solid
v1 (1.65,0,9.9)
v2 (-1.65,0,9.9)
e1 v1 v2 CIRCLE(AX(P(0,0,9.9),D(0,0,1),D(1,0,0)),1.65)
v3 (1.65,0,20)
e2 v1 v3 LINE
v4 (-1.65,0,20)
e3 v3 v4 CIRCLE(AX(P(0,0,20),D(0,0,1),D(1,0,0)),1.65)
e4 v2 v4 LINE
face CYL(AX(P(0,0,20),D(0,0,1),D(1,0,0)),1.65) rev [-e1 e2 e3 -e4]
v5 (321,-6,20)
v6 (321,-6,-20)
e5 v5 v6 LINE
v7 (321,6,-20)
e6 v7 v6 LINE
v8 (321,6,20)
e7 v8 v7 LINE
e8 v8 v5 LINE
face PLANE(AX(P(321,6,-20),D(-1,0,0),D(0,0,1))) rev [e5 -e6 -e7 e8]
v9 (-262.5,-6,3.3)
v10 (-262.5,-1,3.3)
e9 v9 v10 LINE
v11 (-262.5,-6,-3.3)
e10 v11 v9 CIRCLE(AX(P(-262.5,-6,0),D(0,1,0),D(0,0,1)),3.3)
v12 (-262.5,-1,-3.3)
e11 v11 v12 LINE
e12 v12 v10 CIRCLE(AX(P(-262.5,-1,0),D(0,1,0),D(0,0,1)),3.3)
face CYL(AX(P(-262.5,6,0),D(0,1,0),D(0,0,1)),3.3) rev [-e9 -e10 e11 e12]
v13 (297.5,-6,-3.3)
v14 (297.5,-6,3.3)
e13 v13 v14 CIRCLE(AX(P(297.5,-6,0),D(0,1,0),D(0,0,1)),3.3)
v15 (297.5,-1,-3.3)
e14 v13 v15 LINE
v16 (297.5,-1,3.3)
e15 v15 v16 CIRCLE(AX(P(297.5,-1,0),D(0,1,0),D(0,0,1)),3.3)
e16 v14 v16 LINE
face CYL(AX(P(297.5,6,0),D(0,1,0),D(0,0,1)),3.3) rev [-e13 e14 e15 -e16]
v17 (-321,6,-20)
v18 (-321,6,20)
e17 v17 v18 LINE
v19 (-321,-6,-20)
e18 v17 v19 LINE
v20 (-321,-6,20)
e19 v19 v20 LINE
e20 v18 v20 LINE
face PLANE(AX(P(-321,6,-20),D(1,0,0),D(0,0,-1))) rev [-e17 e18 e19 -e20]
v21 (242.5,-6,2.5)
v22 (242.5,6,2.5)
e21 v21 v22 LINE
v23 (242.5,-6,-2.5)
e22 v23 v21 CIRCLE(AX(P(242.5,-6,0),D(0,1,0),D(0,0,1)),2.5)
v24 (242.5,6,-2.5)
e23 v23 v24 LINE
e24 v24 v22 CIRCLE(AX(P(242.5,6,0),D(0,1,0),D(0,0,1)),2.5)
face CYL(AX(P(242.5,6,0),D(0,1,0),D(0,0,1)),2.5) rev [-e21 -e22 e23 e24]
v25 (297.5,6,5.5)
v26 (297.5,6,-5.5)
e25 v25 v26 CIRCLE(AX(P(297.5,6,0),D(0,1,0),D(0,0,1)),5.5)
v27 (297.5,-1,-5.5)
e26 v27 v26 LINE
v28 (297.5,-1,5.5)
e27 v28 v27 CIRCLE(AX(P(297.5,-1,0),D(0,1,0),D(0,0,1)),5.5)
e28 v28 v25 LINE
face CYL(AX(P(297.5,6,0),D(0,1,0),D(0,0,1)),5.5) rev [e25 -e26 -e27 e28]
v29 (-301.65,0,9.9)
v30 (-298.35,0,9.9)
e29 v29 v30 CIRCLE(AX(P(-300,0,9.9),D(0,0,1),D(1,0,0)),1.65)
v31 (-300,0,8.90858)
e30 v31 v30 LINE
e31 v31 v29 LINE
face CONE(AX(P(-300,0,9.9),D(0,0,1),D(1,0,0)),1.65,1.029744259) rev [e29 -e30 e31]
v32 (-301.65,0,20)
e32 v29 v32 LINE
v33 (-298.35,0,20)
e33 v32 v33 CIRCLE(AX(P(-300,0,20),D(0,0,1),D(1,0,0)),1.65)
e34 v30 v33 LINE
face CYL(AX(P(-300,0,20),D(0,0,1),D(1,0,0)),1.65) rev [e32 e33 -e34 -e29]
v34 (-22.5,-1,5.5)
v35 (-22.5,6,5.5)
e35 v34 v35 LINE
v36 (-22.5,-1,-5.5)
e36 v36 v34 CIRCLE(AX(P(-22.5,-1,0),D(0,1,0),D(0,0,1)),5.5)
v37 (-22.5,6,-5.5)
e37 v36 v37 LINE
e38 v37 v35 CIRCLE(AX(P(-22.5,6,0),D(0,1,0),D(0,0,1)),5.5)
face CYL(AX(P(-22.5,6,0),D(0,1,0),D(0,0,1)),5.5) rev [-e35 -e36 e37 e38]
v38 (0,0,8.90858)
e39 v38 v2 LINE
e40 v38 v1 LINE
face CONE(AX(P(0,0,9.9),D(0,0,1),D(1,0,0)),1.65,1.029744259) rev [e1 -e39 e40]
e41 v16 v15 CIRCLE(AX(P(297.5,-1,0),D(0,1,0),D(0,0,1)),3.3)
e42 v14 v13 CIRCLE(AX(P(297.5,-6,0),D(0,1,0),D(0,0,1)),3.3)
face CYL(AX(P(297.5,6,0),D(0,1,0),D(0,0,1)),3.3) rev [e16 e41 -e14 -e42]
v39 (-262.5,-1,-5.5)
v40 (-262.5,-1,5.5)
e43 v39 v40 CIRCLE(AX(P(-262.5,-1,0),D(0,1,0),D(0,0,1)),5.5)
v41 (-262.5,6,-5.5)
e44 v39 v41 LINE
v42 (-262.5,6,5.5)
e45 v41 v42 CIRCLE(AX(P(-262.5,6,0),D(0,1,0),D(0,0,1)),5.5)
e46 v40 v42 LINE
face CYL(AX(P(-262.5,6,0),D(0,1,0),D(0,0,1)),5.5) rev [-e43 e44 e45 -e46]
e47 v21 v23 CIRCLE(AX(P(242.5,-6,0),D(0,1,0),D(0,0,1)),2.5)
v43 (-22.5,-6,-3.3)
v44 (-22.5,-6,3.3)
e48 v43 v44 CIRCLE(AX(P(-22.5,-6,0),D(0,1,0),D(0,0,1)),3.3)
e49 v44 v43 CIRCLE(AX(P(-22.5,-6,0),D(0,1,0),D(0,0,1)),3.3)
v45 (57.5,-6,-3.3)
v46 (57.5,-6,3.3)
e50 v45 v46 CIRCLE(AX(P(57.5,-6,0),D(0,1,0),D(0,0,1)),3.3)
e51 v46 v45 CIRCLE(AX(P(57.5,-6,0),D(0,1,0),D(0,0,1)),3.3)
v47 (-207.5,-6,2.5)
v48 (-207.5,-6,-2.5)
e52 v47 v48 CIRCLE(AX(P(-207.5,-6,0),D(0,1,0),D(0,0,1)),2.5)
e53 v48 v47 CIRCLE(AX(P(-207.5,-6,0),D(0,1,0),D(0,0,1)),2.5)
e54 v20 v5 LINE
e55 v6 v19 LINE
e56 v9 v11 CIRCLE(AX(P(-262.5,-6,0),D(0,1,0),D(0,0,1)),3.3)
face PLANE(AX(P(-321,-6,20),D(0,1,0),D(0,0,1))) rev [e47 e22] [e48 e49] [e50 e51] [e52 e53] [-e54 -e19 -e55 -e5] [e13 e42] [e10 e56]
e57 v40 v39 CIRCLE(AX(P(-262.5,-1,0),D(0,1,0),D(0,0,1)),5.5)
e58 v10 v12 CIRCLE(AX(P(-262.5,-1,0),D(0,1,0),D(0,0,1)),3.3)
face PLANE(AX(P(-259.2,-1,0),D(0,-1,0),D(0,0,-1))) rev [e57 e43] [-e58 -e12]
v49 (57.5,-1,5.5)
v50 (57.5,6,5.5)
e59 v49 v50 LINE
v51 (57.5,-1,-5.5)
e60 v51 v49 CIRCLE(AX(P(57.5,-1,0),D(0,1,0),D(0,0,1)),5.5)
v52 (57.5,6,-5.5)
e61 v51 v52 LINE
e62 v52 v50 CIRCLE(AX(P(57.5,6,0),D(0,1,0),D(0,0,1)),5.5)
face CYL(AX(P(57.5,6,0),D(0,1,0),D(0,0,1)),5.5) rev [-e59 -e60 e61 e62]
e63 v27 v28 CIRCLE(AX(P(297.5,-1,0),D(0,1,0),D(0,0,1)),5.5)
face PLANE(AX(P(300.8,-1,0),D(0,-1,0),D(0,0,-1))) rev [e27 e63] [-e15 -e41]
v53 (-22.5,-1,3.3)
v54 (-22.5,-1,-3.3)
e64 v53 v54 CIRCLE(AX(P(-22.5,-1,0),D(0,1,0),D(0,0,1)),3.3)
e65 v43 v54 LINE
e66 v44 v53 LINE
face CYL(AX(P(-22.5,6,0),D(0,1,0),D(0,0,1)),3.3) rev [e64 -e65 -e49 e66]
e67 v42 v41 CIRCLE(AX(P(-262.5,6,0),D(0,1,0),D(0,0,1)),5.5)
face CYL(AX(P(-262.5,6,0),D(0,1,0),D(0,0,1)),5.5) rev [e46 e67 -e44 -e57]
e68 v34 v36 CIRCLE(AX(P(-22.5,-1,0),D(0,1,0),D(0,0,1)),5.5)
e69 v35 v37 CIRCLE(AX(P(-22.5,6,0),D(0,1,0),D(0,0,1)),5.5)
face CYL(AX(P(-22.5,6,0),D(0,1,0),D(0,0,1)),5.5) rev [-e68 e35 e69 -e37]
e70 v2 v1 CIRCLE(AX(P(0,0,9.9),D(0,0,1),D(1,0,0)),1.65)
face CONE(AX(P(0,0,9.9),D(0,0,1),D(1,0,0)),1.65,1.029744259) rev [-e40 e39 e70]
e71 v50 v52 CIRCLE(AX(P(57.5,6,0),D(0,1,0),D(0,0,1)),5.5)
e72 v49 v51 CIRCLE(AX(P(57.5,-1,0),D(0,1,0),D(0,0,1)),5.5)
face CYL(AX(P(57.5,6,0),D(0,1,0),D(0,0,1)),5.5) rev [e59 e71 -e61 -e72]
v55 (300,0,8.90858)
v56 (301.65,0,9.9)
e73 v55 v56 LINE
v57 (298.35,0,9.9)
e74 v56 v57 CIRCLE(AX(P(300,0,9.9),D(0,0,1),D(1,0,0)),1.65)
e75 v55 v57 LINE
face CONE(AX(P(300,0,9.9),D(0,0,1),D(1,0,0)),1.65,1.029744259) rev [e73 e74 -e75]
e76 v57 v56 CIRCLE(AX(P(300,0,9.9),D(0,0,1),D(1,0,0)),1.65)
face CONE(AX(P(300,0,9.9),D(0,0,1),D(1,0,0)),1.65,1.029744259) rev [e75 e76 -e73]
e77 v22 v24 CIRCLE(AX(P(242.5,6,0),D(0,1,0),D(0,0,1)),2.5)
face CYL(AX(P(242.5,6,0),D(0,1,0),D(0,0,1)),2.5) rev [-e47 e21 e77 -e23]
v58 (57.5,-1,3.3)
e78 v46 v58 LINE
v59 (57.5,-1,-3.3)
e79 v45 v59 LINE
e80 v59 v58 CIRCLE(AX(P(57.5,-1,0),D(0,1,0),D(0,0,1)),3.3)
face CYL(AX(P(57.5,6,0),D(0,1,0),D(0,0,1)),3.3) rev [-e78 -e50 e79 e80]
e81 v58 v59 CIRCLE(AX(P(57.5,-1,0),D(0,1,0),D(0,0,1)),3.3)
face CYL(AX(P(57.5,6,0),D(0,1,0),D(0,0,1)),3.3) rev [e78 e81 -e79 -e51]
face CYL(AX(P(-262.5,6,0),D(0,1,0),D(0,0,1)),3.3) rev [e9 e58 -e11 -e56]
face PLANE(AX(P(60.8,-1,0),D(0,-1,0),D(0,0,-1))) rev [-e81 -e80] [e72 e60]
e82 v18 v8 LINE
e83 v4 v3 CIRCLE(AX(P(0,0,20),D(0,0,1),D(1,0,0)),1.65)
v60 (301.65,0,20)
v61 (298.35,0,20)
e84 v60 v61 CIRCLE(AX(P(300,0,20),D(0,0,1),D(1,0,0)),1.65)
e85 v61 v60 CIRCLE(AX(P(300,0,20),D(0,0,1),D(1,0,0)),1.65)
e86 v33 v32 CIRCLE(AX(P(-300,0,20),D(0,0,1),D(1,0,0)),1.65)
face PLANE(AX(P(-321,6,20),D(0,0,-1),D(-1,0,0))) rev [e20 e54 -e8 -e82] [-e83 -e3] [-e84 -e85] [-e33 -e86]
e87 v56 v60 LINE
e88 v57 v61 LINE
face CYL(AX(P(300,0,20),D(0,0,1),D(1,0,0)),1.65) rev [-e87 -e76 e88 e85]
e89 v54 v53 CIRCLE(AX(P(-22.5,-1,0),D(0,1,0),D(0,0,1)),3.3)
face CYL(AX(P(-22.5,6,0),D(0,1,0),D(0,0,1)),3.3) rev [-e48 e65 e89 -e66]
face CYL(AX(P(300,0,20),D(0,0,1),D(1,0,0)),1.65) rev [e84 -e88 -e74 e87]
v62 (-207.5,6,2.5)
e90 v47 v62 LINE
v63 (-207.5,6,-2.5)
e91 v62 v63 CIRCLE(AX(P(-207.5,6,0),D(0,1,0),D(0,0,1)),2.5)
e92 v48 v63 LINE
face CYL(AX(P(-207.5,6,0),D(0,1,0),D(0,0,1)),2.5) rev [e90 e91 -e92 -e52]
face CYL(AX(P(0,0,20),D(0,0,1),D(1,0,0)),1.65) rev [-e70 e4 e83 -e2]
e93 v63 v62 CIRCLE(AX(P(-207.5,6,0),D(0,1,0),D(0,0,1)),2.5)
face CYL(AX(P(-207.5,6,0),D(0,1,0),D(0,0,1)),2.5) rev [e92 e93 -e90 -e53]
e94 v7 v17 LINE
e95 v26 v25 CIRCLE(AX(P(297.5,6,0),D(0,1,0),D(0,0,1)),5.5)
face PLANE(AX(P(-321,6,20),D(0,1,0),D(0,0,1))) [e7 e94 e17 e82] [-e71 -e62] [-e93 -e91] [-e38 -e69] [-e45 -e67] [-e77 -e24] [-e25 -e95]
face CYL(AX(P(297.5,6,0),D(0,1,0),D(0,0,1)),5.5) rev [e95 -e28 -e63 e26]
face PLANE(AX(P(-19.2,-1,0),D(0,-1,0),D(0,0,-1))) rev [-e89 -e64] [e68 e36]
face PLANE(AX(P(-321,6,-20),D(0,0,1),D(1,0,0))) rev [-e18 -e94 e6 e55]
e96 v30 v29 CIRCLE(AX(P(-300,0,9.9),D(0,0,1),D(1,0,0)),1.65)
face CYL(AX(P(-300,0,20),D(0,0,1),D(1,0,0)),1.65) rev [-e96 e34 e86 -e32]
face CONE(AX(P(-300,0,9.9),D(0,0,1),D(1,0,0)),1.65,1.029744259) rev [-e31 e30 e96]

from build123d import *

# Parameters (mm, degrees)
SKETCH1_W                                         = 642
SKETCH1_H                                         = 40
EXTRUDE1_DEPTH                                    = 6
M6_SOCKET_HEAD_CAP_SCREW_COUNTERBORE1_D           = 6.6
M6_SOCKET_HEAD_CAP_SCREW_COUNTERBORE1_CBORE_D     = 11
M6_SOCKET_HEAD_CAP_SCREW_COUNTERBORE1_CBORE_DEPTH = 7
M4_TAPPED_HOLE1_D                                 = 3.3
M4_TAPPED_HOLE1_DEPTH                             = 10.1
M4_TAPPED_HOLE1_TIP                               = 0.991420021
M6_TAPPED_HOLE1_D                                 = 5


with BuildPart() as part:
    # Sketch1 → Extrude1 (new, symmetric)
    with BuildSketch(Plane(origin=(0, 0, 0), x_dir=(1, 0, 0), z_dir=(0, 1, 0))):
        Rectangle(SKETCH1_W, SKETCH1_H)
    extrude(amount=EXTRUDE1_DEPTH, both=True)

    # M6 Socket Head Cap Screw Counterbore1 (through all)
    with Locations(Plane(origin=(-262.5, 6, 0), x_dir=(0, 0, 1), z_dir=(0, 1, 0))):
        with Locations((0, 0), (0, 240), (0, 320), (0, 560)):
            CounterBoreHole(M6_SOCKET_HEAD_CAP_SCREW_COUNTERBORE1_D / 2, M6_SOCKET_HEAD_CAP_SCREW_COUNTERBORE1_CBORE_D / 2, M6_SOCKET_HEAD_CAP_SCREW_COUNTERBORE1_CBORE_DEPTH)

    # M4 Tapped Hole1
    with Locations(Plane(origin=(300, 0, 20), x_dir=(1, 0, 0), z_dir=(0, 0, 1))):
        with Locations((0, 0), (-300, 0), (-600, 0)):
            Hole(M4_TAPPED_HOLE1_D / 2, depth=M4_TAPPED_HOLE1_DEPTH)
            with Locations((0, 0, -(M4_TAPPED_HOLE1_DEPTH + M4_TAPPED_HOLE1_TIP / 2))):  # 118° drill point
                Cone(0, M4_TAPPED_HOLE1_D / 2, M4_TAPPED_HOLE1_TIP, mode=Mode.SUBTRACT)

    # M6 Tapped Hole1 (through all)
    with Locations(Plane(origin=(-207.5, 6, 0), x_dir=(0, 0, 1), z_dir=(0, 1, 0))):
        with Locations((0, 0), (0, 450)):
            Hole(M6_TAPPED_HOLE1_D / 2)


solid = part.part
